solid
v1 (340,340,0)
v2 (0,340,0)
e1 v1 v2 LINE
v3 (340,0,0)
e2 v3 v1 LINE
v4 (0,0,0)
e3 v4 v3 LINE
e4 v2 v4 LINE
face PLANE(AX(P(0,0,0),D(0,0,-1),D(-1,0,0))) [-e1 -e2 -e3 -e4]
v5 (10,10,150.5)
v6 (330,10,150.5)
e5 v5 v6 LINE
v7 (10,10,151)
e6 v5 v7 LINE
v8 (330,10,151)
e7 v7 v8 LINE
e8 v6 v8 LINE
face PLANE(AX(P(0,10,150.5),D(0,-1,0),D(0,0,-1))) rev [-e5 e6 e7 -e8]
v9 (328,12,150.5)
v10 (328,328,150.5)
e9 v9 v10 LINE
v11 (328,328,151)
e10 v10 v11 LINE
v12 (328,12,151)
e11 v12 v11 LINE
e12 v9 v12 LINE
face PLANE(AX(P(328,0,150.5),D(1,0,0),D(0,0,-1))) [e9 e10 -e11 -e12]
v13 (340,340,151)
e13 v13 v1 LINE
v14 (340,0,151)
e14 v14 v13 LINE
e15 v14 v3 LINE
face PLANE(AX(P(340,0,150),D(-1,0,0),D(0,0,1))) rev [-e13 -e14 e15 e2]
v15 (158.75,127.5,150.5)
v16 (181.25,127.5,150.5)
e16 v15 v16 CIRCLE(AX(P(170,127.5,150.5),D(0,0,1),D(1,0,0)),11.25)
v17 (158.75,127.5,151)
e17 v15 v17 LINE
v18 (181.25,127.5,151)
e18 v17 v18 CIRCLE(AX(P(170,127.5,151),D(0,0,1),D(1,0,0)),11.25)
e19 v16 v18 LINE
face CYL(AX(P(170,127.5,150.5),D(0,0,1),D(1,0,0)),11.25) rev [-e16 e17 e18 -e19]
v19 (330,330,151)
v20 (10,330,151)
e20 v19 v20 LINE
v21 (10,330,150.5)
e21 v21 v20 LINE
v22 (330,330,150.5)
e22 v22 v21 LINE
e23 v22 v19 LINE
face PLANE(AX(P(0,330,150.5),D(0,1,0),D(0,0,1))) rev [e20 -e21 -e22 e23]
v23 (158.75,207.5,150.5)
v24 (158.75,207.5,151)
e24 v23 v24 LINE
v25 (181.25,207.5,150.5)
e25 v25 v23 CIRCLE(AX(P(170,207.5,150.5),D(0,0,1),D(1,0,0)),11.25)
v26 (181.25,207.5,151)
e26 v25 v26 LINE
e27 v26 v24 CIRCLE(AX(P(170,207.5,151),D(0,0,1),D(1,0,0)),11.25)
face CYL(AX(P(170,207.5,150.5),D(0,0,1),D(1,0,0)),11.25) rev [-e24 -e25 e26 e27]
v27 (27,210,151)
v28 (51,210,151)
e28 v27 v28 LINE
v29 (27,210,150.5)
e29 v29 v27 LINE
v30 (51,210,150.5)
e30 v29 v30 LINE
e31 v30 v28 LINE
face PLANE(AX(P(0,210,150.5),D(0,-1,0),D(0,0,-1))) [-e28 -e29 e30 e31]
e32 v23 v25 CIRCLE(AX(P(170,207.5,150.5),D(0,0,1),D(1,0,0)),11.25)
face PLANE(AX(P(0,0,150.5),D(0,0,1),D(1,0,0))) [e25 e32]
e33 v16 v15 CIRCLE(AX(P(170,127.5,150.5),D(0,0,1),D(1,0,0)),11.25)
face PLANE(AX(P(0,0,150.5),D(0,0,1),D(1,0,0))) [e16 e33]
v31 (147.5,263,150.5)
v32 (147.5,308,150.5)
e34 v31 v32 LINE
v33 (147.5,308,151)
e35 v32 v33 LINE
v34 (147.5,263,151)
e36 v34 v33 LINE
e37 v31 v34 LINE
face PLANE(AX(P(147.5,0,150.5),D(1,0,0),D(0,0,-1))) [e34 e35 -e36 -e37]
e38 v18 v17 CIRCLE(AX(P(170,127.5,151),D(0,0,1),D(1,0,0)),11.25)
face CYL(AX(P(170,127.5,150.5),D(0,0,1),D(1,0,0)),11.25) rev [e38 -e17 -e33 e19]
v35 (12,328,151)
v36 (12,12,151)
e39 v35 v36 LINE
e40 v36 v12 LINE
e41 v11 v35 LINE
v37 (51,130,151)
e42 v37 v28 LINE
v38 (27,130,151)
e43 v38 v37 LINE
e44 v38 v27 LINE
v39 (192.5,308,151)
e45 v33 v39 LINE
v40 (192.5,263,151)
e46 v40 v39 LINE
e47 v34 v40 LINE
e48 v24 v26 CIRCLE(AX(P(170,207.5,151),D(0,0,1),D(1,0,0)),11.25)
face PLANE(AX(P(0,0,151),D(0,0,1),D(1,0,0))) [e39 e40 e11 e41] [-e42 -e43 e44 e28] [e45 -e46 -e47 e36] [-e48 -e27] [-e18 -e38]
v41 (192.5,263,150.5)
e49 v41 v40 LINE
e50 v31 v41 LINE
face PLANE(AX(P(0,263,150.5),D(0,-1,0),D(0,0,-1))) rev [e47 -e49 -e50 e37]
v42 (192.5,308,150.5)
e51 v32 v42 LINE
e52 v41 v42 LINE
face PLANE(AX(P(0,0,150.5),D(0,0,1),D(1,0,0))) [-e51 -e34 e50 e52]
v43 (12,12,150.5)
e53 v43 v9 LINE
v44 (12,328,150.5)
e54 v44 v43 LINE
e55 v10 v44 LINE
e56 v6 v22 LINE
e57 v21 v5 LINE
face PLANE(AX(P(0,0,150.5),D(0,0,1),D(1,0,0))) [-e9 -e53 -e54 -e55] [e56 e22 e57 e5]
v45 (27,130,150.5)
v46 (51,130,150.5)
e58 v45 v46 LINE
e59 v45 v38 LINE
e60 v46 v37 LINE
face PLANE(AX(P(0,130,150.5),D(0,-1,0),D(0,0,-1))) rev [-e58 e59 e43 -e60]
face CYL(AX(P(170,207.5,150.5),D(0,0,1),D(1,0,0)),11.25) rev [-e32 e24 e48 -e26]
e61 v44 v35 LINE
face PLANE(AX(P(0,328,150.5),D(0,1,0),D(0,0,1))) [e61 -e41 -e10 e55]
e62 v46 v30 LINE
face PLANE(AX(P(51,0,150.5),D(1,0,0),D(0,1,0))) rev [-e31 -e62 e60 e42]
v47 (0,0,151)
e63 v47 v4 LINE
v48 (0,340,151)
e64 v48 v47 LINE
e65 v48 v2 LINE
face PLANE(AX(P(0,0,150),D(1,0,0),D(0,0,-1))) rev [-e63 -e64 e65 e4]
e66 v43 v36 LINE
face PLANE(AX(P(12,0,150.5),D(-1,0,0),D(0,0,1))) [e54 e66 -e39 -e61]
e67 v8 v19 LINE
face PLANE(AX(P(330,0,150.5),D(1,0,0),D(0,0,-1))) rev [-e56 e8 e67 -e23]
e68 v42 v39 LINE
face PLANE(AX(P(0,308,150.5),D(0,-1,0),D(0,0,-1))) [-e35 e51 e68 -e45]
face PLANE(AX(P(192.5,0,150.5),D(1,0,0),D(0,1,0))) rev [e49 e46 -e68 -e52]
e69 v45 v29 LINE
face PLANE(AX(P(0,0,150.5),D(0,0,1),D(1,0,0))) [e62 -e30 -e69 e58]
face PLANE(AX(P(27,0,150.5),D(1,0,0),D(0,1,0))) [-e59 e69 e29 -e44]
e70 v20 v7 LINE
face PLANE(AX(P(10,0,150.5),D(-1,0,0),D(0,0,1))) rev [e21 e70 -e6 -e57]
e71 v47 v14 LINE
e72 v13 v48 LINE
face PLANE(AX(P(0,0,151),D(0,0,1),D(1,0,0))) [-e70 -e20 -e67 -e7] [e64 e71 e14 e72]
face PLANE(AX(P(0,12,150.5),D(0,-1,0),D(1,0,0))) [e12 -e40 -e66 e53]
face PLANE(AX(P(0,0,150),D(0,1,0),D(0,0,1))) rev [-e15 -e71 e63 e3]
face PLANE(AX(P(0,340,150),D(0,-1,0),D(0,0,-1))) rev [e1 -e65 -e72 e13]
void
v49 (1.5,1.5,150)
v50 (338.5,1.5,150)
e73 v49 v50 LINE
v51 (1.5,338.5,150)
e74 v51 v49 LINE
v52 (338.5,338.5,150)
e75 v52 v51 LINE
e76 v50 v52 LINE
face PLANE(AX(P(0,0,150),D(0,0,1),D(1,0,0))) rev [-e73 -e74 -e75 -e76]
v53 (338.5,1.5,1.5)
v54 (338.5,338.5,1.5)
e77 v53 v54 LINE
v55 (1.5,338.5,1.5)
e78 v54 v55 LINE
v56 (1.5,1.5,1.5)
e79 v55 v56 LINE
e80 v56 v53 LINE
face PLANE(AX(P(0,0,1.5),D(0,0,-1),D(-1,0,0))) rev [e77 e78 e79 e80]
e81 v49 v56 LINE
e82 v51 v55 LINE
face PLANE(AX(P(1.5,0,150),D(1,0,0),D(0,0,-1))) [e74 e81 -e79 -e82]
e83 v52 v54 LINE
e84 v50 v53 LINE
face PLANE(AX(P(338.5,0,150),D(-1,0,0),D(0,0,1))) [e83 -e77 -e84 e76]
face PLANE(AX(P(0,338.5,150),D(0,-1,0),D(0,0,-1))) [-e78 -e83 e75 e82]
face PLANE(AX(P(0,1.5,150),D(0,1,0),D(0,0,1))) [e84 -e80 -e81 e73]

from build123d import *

# Parameters (mm, degrees)
SKETCH1_W           = 340
SKETCH1_H           = 340
BOSS_EXTRUDE1_DEPTH = 150
SHELL1_T            = -1.5
SKETCH2_W           = 340
SKETCH2_H           = 340
BOSS_EXTRUDE2_DEPTH = 1
SKETCH3_W           = 320
SKETCH3_H           = 320
SKETCH3_W_2         = 316
SKETCH3_H_2         = 316
SKETCH3_R           = 11.25
SKETCH3_W_3         = 24
SKETCH3_H_3         = 80
SKETCH3_W_4         = 45
SKETCH3_H_4         = 45
CUT_EXTRUDE1_DEPTH  = 0.5


with BuildPart() as part:
    # Sketch1 → Boss-Extrude1 (new body)
    with BuildSketch(Plane.XY):
        with Locations((170, 170)):
            Rectangle(SKETCH1_W, SKETCH1_H)
    extrude(amount=BOSS_EXTRUDE1_DEPTH)

    # Shell1
    shell1_openings = [part.faces().sort_by_distance(p)[0] for p in [
        (170, 170, 150),
    ]]
    offset(amount=SHELL1_T, openings=shell1_openings, kind=Kind.INTERSECTION)

    # Sketch2 → Boss-Extrude2 (add)
    with BuildSketch(Plane.XY.offset(150)):
        with Locations((170, 170)):
            Rectangle(SKETCH2_W, SKETCH2_H)
    extrude(amount=BOSS_EXTRUDE2_DEPTH)

    # Sketch3 → Cut-Extrude1 (cut)
    # profile 1 of 5: a face of its own
    with BuildSketch(Plane.XY.offset(151)):
        with Locations((170, 170)):
            Rectangle(SKETCH3_W, SKETCH3_H)
        with Locations((170, 170)):
            Rectangle(SKETCH3_W_2, SKETCH3_H_2, mode=Mode.SUBTRACT)
    # profile 2 of 5: a face of its own
    with BuildSketch(Plane.XY.offset(151)):
        with Locations((170, 207.5)):
            Circle(SKETCH3_R)
    # profile 3 of 5: a face of its own
    with BuildSketch(Plane.XY.offset(151)):
        with Locations((170, 127.5)):
            Circle(SKETCH3_R)
    # profile 4 of 5: a face of its own
    with BuildSketch(Plane.XY.offset(151)):
        with Locations((39, 170)):
            Rectangle(SKETCH3_W_3, SKETCH3_H_3)
    # profile 5 of 5: a face of its own
    with BuildSketch(Plane.XY.offset(151)):
        with Locations((170, 285.5)):
            Rectangle(SKETCH3_W_4, SKETCH3_H_4)
    extrude(amount=-CUT_EXTRUDE1_DEPTH, mode=Mode.SUBTRACT)


solid = part.part
